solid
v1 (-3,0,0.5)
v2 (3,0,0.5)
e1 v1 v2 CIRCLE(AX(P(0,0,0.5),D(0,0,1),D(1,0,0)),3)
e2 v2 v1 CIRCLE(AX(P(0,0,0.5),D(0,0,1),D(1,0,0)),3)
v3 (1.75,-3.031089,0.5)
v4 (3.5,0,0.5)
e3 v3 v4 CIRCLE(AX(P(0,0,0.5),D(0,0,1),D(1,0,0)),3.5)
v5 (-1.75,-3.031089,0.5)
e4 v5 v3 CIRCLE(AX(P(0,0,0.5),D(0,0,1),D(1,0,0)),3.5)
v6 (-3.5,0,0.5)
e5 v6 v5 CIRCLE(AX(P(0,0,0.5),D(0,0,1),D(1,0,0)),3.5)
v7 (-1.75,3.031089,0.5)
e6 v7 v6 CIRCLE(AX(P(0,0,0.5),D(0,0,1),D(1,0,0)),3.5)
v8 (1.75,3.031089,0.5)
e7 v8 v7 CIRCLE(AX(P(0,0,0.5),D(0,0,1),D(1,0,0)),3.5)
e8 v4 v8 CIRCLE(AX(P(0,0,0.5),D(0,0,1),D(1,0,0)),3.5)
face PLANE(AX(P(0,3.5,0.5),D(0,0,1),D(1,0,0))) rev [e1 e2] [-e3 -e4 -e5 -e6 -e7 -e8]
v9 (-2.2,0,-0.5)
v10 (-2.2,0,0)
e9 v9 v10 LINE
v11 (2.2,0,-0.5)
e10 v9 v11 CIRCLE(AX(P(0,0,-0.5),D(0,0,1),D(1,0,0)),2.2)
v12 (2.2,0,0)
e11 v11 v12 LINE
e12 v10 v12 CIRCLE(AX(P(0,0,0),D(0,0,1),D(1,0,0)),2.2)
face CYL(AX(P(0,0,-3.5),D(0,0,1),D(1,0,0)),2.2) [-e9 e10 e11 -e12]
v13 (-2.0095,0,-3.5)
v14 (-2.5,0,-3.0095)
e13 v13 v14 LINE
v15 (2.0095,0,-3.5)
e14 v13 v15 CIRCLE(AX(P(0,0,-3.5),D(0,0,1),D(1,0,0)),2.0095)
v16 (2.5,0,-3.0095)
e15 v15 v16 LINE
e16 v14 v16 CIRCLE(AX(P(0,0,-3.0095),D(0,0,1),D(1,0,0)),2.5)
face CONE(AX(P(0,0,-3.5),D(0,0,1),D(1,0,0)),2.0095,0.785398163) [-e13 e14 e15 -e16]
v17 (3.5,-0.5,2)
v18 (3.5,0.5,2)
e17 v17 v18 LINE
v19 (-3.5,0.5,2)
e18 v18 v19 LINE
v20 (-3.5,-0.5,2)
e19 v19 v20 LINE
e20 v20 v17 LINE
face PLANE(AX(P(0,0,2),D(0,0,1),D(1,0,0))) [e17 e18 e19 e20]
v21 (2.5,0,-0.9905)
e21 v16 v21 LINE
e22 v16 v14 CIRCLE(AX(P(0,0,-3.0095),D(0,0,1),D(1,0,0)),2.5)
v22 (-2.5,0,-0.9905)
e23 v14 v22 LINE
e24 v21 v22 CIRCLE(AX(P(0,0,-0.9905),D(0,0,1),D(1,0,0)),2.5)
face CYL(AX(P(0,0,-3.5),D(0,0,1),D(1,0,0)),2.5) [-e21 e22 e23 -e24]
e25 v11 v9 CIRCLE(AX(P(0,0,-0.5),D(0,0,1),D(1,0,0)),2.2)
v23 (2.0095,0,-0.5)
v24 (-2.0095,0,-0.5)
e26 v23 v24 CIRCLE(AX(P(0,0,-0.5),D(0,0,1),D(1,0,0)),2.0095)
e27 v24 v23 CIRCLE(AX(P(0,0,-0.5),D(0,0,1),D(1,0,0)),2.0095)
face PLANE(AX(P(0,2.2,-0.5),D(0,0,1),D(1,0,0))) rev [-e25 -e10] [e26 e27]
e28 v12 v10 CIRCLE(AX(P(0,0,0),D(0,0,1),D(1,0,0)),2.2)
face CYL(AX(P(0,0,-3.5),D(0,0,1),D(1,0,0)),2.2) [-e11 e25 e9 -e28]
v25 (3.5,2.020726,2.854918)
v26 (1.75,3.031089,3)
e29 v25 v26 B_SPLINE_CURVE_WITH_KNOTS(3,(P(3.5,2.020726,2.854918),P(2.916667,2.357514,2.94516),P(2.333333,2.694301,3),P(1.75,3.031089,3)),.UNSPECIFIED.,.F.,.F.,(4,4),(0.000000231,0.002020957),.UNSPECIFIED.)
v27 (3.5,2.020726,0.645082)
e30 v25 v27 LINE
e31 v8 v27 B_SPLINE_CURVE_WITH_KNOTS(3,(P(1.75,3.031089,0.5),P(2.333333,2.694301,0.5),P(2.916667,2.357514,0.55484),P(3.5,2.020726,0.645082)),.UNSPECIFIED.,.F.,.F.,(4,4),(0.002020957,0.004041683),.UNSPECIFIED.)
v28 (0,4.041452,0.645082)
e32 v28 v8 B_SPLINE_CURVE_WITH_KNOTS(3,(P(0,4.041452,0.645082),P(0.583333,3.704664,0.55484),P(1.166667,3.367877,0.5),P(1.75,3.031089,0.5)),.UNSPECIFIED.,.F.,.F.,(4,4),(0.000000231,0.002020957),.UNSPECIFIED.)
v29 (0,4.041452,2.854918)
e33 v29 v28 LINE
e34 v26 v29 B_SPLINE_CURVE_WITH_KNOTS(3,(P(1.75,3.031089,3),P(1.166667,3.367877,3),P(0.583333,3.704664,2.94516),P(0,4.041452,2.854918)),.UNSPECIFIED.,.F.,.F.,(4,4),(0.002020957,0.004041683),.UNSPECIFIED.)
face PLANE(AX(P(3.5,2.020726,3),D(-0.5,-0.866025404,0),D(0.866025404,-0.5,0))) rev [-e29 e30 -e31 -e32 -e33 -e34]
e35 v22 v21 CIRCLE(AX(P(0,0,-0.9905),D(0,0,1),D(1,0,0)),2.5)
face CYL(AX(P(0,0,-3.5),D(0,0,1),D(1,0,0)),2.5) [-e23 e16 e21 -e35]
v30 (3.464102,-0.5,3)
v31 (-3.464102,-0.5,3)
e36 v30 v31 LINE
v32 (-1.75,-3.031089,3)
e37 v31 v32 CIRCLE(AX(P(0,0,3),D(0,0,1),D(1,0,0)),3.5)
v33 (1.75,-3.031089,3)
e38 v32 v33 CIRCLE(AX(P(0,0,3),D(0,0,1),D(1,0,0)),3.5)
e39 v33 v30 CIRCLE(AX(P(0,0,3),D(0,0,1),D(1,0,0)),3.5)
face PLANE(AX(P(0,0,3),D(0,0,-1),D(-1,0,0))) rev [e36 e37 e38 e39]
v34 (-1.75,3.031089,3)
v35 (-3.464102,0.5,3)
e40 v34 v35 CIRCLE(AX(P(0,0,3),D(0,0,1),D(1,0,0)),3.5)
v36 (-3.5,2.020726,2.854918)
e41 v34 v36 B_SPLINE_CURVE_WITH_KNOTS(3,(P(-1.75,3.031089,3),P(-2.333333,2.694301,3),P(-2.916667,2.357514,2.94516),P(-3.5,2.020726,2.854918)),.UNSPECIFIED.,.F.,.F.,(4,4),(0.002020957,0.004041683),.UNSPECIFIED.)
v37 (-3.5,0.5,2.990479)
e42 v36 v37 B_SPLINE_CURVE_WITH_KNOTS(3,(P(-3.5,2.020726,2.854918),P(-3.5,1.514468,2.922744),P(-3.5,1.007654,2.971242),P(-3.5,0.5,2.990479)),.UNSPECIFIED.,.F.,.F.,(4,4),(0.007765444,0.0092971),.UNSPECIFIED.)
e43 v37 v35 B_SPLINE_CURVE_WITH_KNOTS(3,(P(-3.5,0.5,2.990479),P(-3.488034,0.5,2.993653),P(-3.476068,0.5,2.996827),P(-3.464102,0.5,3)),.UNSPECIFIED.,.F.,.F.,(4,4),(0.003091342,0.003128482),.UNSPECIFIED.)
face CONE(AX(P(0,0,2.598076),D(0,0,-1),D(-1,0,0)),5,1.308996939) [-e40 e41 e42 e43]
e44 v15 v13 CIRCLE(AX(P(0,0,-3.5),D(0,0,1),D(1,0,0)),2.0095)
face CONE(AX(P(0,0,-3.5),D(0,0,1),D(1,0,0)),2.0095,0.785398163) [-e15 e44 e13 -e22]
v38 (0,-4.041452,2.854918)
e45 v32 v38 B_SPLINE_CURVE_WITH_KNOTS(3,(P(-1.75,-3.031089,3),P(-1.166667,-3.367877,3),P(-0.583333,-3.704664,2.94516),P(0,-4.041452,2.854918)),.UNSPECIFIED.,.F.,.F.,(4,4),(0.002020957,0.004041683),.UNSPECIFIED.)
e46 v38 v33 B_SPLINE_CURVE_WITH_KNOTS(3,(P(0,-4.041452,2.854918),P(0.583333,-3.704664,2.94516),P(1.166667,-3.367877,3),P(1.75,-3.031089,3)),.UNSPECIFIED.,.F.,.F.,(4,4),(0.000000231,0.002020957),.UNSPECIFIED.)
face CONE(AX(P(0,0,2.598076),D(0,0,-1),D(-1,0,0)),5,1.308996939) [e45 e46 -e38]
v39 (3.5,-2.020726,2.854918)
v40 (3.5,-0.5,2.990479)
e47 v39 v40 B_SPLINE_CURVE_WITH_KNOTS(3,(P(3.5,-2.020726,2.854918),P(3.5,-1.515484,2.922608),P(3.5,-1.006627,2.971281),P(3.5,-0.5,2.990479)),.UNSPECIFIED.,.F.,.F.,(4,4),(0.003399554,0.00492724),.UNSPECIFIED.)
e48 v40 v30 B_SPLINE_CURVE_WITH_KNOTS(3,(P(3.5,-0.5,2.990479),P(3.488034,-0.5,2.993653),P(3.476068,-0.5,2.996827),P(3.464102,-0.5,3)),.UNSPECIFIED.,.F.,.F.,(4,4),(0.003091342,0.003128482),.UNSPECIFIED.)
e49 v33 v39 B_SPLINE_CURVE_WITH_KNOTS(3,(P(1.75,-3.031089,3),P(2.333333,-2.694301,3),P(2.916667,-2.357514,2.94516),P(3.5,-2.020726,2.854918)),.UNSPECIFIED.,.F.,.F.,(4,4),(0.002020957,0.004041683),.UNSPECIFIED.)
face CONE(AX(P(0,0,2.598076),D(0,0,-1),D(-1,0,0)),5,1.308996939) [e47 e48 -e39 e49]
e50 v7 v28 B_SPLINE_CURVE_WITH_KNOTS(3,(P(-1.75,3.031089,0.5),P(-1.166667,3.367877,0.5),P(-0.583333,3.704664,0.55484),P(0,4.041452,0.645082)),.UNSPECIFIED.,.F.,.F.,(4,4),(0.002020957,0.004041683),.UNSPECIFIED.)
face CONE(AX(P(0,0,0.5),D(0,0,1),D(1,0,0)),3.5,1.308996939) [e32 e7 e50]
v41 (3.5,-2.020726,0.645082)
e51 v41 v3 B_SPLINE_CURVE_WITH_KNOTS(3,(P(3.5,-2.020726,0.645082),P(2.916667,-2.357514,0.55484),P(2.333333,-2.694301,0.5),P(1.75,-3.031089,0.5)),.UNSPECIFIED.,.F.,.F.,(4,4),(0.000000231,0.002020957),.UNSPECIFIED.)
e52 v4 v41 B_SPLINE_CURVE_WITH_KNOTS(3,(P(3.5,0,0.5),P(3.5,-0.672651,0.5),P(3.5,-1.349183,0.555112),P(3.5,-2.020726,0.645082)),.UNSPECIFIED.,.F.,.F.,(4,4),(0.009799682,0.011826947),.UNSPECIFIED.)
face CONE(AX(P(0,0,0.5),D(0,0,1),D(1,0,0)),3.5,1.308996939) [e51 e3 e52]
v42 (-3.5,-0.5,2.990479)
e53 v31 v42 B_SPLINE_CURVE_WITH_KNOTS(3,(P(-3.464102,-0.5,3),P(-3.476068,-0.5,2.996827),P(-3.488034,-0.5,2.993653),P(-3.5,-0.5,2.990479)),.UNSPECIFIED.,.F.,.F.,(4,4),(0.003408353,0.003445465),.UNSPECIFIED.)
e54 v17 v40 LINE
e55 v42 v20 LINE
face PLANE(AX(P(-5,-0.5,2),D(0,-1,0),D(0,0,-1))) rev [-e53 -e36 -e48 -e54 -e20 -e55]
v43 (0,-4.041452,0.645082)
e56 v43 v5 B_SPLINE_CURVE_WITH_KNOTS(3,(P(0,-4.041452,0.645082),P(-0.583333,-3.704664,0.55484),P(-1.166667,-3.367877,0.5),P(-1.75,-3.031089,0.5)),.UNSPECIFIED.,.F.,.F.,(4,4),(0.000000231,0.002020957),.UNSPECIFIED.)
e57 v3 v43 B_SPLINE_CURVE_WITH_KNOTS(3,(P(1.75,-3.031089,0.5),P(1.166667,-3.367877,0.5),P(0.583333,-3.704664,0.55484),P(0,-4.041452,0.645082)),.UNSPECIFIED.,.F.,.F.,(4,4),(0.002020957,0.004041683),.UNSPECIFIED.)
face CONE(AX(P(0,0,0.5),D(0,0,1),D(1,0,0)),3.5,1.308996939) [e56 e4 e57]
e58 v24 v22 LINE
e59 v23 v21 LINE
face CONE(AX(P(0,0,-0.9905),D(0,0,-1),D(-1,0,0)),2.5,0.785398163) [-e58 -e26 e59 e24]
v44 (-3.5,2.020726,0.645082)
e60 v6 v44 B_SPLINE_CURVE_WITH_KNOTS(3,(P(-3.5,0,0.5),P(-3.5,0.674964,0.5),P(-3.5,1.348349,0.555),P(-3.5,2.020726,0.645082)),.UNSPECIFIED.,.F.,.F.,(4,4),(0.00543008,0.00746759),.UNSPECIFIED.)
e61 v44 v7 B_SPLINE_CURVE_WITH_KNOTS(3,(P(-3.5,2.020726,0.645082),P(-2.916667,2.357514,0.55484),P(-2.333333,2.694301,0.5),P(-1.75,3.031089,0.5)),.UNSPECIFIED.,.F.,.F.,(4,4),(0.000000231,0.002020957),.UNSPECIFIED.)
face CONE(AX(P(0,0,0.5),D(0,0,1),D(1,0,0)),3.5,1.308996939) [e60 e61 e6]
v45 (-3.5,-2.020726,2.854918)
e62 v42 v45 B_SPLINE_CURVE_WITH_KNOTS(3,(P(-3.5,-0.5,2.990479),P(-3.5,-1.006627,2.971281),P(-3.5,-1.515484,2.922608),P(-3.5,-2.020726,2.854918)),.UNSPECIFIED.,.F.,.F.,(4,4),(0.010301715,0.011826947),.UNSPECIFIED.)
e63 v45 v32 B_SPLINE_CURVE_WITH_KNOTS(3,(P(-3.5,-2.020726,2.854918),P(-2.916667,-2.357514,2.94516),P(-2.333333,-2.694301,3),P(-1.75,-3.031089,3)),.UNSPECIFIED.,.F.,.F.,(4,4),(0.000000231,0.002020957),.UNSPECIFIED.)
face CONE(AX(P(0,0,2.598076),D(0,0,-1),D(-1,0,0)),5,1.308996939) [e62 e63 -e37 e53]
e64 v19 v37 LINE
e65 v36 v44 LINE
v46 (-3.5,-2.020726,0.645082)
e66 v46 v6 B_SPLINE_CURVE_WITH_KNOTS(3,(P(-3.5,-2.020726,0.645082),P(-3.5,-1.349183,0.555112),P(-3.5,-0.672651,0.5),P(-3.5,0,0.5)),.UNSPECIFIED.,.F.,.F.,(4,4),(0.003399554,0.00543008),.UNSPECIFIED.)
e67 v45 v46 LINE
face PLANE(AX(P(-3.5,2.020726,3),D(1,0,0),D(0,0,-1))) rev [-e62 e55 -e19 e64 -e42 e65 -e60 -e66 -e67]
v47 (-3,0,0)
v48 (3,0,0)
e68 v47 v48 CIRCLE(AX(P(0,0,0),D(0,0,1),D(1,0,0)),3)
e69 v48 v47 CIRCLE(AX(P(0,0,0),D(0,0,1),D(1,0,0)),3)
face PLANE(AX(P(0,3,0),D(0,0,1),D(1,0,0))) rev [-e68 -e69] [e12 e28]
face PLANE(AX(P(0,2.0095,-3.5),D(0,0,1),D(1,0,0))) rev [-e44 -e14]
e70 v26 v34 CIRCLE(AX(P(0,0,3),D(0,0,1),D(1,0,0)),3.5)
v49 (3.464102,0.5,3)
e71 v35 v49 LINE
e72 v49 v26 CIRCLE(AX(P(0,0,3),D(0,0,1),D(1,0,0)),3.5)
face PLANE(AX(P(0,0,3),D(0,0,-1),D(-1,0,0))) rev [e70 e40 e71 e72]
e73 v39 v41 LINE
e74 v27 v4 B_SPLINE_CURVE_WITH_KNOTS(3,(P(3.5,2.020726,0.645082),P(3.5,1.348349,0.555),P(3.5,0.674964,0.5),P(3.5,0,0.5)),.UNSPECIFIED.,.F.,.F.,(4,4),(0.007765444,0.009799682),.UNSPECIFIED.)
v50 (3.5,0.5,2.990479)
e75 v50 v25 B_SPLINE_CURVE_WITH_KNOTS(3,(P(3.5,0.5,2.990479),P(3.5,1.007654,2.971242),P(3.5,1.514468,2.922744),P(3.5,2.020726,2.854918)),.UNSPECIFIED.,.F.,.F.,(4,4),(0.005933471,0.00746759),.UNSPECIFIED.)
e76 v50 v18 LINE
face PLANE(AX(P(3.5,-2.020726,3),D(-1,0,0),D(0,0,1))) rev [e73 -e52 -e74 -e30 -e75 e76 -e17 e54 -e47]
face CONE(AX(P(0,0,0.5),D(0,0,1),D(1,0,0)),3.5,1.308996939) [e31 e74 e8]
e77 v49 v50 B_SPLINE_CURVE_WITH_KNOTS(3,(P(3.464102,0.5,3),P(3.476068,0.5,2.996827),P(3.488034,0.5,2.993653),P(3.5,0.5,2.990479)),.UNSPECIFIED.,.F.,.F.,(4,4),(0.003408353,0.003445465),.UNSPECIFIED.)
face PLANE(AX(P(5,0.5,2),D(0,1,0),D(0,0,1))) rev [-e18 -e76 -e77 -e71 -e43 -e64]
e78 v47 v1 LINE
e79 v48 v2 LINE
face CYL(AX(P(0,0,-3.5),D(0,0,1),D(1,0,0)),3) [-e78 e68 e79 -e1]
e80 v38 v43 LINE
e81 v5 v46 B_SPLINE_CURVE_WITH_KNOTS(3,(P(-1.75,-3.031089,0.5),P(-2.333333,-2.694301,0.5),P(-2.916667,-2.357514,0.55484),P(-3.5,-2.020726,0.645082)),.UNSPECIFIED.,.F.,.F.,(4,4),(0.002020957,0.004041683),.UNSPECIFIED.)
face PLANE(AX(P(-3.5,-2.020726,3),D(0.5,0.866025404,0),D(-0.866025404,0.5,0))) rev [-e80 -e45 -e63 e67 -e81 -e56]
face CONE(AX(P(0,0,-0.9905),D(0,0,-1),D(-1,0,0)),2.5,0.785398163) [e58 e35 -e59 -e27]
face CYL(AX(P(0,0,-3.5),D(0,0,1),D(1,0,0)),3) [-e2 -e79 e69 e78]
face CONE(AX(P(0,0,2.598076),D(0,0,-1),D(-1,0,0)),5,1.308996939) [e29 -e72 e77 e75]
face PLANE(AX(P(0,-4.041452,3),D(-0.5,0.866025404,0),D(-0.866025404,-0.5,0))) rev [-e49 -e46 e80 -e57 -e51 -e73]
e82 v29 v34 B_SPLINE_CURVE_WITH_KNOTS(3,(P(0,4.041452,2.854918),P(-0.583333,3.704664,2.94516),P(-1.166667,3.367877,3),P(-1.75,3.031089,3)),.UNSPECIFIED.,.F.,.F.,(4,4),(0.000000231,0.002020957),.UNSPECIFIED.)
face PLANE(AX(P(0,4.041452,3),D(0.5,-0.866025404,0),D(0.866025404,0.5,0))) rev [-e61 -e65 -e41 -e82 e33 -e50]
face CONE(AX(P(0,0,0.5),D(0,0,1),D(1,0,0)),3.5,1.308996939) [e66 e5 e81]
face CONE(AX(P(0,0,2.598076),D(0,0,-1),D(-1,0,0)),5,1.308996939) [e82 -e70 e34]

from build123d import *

# Parameters (mm, degrees)
SKETCH2_R          = 5
CUT_EXTRUDE1_DEPTH = 3
SKETCH3_W          = 10
SKETCH3_H          = 1
CUT_EXTRUDE2_DEPTH = 1


with BuildPart() as part:
    # Sketch1 → Revolve1 (revolve)
    with BuildSketch(Plane(origin=(0, 0, 0), x_dir=(0, 0, -1), z_dir=(1, 0, 0)), mode=Mode.PRIVATE) as revolve1_sk:
        Polygon((-3, 0), (-3, 3.5), (-2.598076211, 5), (-0.901923789, 5), (-0.5, 3.5), (-0.5, 3), (0, 3), (0, 2.2), (0.5, 2.2), (0.5, 2.0095), (0.9905, 2.5), (3.0095, 2.5), (3.5, 2.0095), (3.5, 0), align=None)
    revolve(revolve1_sk.sketch.rotate(Axis((0, 0, -3.5), (0, 0, 1)), 270), axis=Axis((0, 0, -3.5), (0, 0, 1)))

    # Sketch2 → Cut-Extrude1 (cut)
    with BuildSketch(Plane.XY):
        Circle(SKETCH2_R)
        Polygon((-3.5, 2.020725942), (-3.5, -2.020725942), (0, -4.041451884), (3.5, -2.020725942), (3.5, 2.020725942), (0, 4.041451884), align=None, mode=Mode.SUBTRACT)
    extrude(amount=CUT_EXTRUDE1_DEPTH, mode=Mode.SUBTRACT)

    # Sketch3 → Cut-Extrude2 (cut)
    with BuildSketch(Plane.XY.offset(3)):
        Rectangle(SKETCH3_W, SKETCH3_H)
    extrude(amount=-CUT_EXTRUDE2_DEPTH, mode=Mode.SUBTRACT)


solid = part.part
